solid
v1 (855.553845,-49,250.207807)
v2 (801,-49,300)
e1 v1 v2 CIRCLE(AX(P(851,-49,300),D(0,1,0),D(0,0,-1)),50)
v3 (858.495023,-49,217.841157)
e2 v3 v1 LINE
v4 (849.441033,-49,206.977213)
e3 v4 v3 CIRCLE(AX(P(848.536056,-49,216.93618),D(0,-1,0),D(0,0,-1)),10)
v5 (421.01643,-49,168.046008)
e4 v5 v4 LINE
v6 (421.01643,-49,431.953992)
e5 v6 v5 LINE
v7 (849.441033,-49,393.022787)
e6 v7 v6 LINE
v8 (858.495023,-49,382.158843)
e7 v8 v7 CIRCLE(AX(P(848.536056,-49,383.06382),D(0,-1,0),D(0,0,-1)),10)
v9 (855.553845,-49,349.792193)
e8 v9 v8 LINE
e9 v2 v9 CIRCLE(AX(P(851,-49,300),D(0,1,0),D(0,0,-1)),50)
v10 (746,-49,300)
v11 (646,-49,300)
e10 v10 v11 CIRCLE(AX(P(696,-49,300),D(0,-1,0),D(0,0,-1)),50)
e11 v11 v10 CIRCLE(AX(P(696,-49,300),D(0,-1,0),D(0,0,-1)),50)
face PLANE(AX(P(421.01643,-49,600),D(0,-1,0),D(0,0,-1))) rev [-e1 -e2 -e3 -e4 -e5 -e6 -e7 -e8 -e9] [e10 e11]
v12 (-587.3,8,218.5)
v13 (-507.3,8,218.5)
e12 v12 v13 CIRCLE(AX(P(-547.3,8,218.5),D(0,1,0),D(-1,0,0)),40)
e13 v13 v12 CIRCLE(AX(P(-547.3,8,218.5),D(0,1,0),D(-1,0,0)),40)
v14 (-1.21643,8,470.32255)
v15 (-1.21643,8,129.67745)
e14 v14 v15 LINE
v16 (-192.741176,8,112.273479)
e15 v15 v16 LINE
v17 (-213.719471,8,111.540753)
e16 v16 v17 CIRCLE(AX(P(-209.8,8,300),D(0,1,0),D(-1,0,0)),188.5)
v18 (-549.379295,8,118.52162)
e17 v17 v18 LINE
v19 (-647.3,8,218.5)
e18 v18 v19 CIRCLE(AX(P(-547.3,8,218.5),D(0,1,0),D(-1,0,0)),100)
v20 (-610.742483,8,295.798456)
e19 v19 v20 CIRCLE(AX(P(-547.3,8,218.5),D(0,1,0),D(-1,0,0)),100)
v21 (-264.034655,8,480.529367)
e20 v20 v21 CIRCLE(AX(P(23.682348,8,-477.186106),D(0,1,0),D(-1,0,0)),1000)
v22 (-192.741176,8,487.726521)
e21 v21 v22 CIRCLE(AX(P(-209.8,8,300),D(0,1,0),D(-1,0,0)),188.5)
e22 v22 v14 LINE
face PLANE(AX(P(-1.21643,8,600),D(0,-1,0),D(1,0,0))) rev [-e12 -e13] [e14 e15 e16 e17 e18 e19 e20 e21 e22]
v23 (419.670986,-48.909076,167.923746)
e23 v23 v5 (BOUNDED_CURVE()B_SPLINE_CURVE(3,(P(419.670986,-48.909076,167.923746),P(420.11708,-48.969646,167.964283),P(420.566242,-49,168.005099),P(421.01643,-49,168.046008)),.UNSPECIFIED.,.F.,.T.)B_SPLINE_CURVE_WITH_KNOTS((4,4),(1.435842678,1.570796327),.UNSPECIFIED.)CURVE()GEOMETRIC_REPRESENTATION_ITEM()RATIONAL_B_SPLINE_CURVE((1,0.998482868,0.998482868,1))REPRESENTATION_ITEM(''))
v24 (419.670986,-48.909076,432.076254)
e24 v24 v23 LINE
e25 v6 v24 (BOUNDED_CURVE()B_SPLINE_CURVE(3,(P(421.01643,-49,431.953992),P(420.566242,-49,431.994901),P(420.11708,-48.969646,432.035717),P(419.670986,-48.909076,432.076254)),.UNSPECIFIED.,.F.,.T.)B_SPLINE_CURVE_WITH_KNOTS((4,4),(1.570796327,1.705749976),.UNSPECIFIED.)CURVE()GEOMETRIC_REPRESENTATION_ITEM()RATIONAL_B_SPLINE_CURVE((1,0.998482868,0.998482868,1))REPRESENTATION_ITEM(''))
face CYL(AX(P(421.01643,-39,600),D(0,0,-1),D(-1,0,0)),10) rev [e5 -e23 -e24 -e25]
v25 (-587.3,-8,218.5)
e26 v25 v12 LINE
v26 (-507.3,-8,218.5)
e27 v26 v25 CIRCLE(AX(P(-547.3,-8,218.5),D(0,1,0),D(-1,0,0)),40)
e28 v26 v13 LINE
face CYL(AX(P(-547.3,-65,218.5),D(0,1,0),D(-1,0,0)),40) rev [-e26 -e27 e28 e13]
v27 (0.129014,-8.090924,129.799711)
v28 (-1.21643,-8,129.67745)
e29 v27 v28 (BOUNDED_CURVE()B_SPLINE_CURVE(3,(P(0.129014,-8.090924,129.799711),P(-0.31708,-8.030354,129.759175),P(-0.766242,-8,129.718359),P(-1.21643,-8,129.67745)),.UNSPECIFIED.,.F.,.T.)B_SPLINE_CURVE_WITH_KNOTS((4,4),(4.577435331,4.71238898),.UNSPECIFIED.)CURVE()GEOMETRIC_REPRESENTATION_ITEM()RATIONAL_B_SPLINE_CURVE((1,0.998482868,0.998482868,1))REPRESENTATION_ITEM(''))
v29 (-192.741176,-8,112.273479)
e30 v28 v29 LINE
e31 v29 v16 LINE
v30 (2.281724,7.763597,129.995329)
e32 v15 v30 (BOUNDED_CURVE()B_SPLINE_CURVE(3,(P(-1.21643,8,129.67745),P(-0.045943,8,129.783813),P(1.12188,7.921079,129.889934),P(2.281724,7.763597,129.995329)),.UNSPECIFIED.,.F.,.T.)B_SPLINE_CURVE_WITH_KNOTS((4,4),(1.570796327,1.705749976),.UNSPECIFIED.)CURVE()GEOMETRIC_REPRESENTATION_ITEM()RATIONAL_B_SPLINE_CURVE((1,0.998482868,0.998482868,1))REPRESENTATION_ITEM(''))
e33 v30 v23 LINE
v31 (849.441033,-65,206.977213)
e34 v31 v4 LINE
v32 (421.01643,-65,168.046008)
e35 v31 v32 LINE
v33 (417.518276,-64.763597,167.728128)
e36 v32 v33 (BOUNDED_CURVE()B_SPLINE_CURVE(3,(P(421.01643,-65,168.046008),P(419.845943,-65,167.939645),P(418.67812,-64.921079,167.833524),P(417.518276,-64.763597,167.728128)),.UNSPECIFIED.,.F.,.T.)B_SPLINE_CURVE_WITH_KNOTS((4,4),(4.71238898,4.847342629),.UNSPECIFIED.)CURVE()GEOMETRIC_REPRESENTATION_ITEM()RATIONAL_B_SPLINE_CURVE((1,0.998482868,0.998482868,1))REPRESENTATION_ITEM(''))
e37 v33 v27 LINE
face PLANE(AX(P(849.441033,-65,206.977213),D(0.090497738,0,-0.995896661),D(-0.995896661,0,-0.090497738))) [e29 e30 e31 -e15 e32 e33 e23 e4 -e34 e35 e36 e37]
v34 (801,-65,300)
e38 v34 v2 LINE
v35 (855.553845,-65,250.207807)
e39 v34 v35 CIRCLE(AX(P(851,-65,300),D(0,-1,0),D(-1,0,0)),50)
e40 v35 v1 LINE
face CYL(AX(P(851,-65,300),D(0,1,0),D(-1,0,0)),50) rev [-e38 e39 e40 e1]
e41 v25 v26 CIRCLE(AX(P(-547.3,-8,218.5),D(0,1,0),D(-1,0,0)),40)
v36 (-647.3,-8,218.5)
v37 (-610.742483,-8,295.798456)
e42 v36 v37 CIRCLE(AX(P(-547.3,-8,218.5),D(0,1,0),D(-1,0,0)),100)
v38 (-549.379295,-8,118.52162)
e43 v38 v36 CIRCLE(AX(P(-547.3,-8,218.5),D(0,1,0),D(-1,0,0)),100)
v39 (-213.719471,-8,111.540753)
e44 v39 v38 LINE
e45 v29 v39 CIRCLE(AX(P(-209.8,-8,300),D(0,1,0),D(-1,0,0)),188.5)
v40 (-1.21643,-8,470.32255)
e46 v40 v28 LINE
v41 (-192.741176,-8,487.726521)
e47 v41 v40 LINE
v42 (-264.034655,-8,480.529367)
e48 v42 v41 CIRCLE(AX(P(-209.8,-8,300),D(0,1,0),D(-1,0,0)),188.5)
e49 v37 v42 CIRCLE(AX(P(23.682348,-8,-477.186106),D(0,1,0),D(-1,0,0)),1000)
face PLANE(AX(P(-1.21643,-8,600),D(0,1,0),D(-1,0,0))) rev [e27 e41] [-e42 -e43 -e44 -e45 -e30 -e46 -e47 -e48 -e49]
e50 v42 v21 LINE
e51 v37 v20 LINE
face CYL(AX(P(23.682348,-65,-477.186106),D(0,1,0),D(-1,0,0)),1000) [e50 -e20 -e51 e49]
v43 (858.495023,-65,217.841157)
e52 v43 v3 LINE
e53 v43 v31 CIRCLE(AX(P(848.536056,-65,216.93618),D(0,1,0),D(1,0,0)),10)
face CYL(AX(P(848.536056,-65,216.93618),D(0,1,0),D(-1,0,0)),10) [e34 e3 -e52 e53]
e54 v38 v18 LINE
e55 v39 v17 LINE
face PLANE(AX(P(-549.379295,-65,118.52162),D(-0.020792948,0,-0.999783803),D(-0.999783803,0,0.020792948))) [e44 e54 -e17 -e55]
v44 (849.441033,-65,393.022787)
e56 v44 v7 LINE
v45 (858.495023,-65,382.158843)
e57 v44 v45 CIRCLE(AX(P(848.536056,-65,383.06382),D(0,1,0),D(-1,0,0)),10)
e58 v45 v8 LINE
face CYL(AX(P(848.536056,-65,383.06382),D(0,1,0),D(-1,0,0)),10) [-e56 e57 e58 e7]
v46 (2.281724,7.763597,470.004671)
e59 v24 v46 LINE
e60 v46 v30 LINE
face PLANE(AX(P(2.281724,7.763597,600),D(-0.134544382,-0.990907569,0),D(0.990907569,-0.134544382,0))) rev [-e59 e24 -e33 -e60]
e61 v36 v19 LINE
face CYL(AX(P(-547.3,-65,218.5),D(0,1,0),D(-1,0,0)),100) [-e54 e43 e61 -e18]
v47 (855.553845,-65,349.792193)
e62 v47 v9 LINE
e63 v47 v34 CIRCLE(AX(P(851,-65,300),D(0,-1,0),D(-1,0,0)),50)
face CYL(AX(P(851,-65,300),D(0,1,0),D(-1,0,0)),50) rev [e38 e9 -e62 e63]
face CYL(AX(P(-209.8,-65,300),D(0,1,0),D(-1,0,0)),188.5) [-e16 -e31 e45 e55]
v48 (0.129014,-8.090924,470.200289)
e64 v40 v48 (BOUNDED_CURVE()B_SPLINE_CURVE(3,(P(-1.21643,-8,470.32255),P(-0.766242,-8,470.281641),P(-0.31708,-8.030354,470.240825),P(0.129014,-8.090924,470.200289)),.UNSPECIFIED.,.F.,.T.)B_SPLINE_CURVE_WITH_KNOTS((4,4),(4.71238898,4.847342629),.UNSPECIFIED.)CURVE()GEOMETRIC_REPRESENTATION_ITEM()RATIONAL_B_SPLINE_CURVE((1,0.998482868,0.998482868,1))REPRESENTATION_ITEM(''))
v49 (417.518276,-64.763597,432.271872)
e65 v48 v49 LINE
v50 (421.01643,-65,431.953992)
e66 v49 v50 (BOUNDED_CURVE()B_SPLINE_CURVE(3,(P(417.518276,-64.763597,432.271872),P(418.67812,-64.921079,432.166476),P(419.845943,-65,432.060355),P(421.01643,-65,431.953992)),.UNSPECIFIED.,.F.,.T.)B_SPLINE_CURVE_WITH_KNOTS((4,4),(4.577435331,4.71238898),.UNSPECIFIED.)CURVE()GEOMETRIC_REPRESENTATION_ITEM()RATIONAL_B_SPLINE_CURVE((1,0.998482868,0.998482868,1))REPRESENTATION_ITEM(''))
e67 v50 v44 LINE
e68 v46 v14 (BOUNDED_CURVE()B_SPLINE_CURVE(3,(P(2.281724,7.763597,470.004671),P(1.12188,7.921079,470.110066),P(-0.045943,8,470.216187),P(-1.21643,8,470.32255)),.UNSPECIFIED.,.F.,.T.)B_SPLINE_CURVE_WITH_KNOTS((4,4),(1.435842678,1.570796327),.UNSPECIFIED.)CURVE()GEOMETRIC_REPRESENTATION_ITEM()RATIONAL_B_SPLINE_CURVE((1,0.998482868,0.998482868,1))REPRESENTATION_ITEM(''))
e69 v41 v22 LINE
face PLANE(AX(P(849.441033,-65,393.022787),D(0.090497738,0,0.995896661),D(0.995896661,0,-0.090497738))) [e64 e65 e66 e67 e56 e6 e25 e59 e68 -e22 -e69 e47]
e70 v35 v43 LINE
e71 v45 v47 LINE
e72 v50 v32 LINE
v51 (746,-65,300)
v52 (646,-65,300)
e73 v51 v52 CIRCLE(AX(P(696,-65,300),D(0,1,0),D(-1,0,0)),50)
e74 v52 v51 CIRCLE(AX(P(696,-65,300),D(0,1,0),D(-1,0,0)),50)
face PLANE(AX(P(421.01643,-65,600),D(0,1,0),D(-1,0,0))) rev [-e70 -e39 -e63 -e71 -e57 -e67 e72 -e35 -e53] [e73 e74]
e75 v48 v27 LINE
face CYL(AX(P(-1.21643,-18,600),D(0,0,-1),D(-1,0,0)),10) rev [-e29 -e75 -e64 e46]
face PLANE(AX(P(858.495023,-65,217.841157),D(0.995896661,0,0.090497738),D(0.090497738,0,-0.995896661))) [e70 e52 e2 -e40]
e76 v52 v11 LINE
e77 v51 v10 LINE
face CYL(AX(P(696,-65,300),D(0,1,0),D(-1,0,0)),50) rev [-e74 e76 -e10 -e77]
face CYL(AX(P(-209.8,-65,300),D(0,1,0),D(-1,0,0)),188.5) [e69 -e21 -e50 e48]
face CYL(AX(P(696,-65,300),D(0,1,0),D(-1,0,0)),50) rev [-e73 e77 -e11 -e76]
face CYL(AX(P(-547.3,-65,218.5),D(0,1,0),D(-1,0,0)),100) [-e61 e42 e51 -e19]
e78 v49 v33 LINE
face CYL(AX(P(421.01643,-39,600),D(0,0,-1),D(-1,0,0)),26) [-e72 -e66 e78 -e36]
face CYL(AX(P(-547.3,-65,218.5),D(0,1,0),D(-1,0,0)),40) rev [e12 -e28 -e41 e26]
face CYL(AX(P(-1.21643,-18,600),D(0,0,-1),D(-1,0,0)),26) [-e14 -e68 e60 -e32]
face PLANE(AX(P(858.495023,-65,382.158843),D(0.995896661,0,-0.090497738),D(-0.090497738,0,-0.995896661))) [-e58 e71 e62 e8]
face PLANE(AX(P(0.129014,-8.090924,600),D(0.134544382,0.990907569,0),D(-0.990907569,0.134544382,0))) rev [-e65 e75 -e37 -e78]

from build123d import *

# Parameters (mm, degrees)
BOSS_EXTRUDE1_DEPTH = 600
SKETCH4_OUTSIDE_W   = 1933.152
SKETCH4_OUTSIDE_H   = 942.352
SKETCH4_OUTSIDE_R   = 40
SKETCH4_OUTSIDE_R_2 = 50
CUT_EXTRUDE1_DEPTH  = 1121.500446229


with BuildPart() as part:
    # Sketch1 → Boss-Extrude1 (new body)
    with BuildSketch(Plane.XY):
        with BuildLine():
            Line((-1.216429586, 8), (-647.3, 8))
            Line((-647.3, 8), (-647.3, -8))
            Line((-647.3, -8), (-1.216429586, -8))
            ThreePointArc((-1.216429586, -8), (-0.542173275, -8.022756973), (0.12901423, -8.090924315))
            Line((0.12901423, -8.090924315), (417.518275664, -64.763596782))
            ThreePointArc((417.518275664, -64.763596782), (419.263363176, -64.940831871), (421.016429586, -65))
            Line((421.016429586, -65), (943.5, -65))
            Line((943.5, -65), (943.5, -49))
            Line((943.5, -49), (421.016429586, -49))
            ThreePointArc((421.016429586, -49), (420.342173275, -48.977243027), (419.67098577, -48.909075685))
            Line((419.67098577, -48.909075685), (2.281724336, 7.763596782))
            ThreePointArc((2.281724336, 7.763596782), (0.536636824, 7.940831871), (-1.216429586, 8))
        make_face()
    extrude(amount=BOSS_EXTRUDE1_DEPTH)

    # Sketch4 outside → Cut-Extrude1 (cut, through all)
    # profile 1 of 3: a face of its own
    with BuildSketch(Plane(origin=(0, 8, 0), x_dir=(1, 0, 0), z_dir=(0, 1, 0))):
        with Locations((148.1, -300)):
            Rectangle(SKETCH4_OUTSIDE_W, SKETCH4_OUTSIDE_H)
        with BuildLine():
            Line((849.441033389, -393.022786976), (-192.741176471, -487.726520609))
            ThreePointArc((-192.741176471, -487.726520609), (-228.733049722, -487.54676651), (-264.034655196, -480.529366519))
            ThreePointArc((-264.034655196, -480.529366519), (-446.549262984, -405.356942265), (-610.742483166, -295.798456192))
            ThreePointArc((-610.742483166, -295.798456192), (-641.798915546, -185.789833988), (-549.379294824, -118.521619672))
            Line((-549.379294824, -118.521619672), (-213.719470744, -111.540753082))
            ThreePointArc((-213.719470744, -111.540753082), (-203.220116273, -111.614875507), (-192.741176471, -112.273479391))
            Line((-192.741176471, -112.273479391), (849.441033389, -206.977213024))
            ThreePointArc((849.441033389, -206.977213024), (856.218024477, -210.53404245), (858.495022624, -217.84115701))
            Line((858.495022624, -217.84115701), (855.553845389, -250.207806915))
            ThreePointArc((855.553845389, -250.207806915), (801, -300), (855.553845389, -349.792193085))
            Line((855.553845389, -349.792193085), (858.495022624, -382.15884299))
            ThreePointArc((858.495022624, -382.15884299), (856.218024477, -389.46595755), (849.441033389, -393.022786976))
        make_face(mode=Mode.SUBTRACT)
    # profile 2 of 3: a face of its own
    with BuildSketch(Plane(origin=(0, 8, 0), x_dir=(1, 0, 0), z_dir=(0, 1, 0))):
        with Locations(Location((-547.3, -218.5, 0), (0, 0, 180))):
            Circle(SKETCH4_OUTSIDE_R)
    # profile 3 of 3: a face of its own
    with BuildSketch(Plane(origin=(0, 8, 0), x_dir=(1, 0, 0), z_dir=(0, 1, 0))):
        with Locations(Location((696, -300, 0), (0, 0, 180))):
            Circle(SKETCH4_OUTSIDE_R_2)
    extrude(amount=-CUT_EXTRUDE1_DEPTH, mode=Mode.SUBTRACT)


solid = part.part
